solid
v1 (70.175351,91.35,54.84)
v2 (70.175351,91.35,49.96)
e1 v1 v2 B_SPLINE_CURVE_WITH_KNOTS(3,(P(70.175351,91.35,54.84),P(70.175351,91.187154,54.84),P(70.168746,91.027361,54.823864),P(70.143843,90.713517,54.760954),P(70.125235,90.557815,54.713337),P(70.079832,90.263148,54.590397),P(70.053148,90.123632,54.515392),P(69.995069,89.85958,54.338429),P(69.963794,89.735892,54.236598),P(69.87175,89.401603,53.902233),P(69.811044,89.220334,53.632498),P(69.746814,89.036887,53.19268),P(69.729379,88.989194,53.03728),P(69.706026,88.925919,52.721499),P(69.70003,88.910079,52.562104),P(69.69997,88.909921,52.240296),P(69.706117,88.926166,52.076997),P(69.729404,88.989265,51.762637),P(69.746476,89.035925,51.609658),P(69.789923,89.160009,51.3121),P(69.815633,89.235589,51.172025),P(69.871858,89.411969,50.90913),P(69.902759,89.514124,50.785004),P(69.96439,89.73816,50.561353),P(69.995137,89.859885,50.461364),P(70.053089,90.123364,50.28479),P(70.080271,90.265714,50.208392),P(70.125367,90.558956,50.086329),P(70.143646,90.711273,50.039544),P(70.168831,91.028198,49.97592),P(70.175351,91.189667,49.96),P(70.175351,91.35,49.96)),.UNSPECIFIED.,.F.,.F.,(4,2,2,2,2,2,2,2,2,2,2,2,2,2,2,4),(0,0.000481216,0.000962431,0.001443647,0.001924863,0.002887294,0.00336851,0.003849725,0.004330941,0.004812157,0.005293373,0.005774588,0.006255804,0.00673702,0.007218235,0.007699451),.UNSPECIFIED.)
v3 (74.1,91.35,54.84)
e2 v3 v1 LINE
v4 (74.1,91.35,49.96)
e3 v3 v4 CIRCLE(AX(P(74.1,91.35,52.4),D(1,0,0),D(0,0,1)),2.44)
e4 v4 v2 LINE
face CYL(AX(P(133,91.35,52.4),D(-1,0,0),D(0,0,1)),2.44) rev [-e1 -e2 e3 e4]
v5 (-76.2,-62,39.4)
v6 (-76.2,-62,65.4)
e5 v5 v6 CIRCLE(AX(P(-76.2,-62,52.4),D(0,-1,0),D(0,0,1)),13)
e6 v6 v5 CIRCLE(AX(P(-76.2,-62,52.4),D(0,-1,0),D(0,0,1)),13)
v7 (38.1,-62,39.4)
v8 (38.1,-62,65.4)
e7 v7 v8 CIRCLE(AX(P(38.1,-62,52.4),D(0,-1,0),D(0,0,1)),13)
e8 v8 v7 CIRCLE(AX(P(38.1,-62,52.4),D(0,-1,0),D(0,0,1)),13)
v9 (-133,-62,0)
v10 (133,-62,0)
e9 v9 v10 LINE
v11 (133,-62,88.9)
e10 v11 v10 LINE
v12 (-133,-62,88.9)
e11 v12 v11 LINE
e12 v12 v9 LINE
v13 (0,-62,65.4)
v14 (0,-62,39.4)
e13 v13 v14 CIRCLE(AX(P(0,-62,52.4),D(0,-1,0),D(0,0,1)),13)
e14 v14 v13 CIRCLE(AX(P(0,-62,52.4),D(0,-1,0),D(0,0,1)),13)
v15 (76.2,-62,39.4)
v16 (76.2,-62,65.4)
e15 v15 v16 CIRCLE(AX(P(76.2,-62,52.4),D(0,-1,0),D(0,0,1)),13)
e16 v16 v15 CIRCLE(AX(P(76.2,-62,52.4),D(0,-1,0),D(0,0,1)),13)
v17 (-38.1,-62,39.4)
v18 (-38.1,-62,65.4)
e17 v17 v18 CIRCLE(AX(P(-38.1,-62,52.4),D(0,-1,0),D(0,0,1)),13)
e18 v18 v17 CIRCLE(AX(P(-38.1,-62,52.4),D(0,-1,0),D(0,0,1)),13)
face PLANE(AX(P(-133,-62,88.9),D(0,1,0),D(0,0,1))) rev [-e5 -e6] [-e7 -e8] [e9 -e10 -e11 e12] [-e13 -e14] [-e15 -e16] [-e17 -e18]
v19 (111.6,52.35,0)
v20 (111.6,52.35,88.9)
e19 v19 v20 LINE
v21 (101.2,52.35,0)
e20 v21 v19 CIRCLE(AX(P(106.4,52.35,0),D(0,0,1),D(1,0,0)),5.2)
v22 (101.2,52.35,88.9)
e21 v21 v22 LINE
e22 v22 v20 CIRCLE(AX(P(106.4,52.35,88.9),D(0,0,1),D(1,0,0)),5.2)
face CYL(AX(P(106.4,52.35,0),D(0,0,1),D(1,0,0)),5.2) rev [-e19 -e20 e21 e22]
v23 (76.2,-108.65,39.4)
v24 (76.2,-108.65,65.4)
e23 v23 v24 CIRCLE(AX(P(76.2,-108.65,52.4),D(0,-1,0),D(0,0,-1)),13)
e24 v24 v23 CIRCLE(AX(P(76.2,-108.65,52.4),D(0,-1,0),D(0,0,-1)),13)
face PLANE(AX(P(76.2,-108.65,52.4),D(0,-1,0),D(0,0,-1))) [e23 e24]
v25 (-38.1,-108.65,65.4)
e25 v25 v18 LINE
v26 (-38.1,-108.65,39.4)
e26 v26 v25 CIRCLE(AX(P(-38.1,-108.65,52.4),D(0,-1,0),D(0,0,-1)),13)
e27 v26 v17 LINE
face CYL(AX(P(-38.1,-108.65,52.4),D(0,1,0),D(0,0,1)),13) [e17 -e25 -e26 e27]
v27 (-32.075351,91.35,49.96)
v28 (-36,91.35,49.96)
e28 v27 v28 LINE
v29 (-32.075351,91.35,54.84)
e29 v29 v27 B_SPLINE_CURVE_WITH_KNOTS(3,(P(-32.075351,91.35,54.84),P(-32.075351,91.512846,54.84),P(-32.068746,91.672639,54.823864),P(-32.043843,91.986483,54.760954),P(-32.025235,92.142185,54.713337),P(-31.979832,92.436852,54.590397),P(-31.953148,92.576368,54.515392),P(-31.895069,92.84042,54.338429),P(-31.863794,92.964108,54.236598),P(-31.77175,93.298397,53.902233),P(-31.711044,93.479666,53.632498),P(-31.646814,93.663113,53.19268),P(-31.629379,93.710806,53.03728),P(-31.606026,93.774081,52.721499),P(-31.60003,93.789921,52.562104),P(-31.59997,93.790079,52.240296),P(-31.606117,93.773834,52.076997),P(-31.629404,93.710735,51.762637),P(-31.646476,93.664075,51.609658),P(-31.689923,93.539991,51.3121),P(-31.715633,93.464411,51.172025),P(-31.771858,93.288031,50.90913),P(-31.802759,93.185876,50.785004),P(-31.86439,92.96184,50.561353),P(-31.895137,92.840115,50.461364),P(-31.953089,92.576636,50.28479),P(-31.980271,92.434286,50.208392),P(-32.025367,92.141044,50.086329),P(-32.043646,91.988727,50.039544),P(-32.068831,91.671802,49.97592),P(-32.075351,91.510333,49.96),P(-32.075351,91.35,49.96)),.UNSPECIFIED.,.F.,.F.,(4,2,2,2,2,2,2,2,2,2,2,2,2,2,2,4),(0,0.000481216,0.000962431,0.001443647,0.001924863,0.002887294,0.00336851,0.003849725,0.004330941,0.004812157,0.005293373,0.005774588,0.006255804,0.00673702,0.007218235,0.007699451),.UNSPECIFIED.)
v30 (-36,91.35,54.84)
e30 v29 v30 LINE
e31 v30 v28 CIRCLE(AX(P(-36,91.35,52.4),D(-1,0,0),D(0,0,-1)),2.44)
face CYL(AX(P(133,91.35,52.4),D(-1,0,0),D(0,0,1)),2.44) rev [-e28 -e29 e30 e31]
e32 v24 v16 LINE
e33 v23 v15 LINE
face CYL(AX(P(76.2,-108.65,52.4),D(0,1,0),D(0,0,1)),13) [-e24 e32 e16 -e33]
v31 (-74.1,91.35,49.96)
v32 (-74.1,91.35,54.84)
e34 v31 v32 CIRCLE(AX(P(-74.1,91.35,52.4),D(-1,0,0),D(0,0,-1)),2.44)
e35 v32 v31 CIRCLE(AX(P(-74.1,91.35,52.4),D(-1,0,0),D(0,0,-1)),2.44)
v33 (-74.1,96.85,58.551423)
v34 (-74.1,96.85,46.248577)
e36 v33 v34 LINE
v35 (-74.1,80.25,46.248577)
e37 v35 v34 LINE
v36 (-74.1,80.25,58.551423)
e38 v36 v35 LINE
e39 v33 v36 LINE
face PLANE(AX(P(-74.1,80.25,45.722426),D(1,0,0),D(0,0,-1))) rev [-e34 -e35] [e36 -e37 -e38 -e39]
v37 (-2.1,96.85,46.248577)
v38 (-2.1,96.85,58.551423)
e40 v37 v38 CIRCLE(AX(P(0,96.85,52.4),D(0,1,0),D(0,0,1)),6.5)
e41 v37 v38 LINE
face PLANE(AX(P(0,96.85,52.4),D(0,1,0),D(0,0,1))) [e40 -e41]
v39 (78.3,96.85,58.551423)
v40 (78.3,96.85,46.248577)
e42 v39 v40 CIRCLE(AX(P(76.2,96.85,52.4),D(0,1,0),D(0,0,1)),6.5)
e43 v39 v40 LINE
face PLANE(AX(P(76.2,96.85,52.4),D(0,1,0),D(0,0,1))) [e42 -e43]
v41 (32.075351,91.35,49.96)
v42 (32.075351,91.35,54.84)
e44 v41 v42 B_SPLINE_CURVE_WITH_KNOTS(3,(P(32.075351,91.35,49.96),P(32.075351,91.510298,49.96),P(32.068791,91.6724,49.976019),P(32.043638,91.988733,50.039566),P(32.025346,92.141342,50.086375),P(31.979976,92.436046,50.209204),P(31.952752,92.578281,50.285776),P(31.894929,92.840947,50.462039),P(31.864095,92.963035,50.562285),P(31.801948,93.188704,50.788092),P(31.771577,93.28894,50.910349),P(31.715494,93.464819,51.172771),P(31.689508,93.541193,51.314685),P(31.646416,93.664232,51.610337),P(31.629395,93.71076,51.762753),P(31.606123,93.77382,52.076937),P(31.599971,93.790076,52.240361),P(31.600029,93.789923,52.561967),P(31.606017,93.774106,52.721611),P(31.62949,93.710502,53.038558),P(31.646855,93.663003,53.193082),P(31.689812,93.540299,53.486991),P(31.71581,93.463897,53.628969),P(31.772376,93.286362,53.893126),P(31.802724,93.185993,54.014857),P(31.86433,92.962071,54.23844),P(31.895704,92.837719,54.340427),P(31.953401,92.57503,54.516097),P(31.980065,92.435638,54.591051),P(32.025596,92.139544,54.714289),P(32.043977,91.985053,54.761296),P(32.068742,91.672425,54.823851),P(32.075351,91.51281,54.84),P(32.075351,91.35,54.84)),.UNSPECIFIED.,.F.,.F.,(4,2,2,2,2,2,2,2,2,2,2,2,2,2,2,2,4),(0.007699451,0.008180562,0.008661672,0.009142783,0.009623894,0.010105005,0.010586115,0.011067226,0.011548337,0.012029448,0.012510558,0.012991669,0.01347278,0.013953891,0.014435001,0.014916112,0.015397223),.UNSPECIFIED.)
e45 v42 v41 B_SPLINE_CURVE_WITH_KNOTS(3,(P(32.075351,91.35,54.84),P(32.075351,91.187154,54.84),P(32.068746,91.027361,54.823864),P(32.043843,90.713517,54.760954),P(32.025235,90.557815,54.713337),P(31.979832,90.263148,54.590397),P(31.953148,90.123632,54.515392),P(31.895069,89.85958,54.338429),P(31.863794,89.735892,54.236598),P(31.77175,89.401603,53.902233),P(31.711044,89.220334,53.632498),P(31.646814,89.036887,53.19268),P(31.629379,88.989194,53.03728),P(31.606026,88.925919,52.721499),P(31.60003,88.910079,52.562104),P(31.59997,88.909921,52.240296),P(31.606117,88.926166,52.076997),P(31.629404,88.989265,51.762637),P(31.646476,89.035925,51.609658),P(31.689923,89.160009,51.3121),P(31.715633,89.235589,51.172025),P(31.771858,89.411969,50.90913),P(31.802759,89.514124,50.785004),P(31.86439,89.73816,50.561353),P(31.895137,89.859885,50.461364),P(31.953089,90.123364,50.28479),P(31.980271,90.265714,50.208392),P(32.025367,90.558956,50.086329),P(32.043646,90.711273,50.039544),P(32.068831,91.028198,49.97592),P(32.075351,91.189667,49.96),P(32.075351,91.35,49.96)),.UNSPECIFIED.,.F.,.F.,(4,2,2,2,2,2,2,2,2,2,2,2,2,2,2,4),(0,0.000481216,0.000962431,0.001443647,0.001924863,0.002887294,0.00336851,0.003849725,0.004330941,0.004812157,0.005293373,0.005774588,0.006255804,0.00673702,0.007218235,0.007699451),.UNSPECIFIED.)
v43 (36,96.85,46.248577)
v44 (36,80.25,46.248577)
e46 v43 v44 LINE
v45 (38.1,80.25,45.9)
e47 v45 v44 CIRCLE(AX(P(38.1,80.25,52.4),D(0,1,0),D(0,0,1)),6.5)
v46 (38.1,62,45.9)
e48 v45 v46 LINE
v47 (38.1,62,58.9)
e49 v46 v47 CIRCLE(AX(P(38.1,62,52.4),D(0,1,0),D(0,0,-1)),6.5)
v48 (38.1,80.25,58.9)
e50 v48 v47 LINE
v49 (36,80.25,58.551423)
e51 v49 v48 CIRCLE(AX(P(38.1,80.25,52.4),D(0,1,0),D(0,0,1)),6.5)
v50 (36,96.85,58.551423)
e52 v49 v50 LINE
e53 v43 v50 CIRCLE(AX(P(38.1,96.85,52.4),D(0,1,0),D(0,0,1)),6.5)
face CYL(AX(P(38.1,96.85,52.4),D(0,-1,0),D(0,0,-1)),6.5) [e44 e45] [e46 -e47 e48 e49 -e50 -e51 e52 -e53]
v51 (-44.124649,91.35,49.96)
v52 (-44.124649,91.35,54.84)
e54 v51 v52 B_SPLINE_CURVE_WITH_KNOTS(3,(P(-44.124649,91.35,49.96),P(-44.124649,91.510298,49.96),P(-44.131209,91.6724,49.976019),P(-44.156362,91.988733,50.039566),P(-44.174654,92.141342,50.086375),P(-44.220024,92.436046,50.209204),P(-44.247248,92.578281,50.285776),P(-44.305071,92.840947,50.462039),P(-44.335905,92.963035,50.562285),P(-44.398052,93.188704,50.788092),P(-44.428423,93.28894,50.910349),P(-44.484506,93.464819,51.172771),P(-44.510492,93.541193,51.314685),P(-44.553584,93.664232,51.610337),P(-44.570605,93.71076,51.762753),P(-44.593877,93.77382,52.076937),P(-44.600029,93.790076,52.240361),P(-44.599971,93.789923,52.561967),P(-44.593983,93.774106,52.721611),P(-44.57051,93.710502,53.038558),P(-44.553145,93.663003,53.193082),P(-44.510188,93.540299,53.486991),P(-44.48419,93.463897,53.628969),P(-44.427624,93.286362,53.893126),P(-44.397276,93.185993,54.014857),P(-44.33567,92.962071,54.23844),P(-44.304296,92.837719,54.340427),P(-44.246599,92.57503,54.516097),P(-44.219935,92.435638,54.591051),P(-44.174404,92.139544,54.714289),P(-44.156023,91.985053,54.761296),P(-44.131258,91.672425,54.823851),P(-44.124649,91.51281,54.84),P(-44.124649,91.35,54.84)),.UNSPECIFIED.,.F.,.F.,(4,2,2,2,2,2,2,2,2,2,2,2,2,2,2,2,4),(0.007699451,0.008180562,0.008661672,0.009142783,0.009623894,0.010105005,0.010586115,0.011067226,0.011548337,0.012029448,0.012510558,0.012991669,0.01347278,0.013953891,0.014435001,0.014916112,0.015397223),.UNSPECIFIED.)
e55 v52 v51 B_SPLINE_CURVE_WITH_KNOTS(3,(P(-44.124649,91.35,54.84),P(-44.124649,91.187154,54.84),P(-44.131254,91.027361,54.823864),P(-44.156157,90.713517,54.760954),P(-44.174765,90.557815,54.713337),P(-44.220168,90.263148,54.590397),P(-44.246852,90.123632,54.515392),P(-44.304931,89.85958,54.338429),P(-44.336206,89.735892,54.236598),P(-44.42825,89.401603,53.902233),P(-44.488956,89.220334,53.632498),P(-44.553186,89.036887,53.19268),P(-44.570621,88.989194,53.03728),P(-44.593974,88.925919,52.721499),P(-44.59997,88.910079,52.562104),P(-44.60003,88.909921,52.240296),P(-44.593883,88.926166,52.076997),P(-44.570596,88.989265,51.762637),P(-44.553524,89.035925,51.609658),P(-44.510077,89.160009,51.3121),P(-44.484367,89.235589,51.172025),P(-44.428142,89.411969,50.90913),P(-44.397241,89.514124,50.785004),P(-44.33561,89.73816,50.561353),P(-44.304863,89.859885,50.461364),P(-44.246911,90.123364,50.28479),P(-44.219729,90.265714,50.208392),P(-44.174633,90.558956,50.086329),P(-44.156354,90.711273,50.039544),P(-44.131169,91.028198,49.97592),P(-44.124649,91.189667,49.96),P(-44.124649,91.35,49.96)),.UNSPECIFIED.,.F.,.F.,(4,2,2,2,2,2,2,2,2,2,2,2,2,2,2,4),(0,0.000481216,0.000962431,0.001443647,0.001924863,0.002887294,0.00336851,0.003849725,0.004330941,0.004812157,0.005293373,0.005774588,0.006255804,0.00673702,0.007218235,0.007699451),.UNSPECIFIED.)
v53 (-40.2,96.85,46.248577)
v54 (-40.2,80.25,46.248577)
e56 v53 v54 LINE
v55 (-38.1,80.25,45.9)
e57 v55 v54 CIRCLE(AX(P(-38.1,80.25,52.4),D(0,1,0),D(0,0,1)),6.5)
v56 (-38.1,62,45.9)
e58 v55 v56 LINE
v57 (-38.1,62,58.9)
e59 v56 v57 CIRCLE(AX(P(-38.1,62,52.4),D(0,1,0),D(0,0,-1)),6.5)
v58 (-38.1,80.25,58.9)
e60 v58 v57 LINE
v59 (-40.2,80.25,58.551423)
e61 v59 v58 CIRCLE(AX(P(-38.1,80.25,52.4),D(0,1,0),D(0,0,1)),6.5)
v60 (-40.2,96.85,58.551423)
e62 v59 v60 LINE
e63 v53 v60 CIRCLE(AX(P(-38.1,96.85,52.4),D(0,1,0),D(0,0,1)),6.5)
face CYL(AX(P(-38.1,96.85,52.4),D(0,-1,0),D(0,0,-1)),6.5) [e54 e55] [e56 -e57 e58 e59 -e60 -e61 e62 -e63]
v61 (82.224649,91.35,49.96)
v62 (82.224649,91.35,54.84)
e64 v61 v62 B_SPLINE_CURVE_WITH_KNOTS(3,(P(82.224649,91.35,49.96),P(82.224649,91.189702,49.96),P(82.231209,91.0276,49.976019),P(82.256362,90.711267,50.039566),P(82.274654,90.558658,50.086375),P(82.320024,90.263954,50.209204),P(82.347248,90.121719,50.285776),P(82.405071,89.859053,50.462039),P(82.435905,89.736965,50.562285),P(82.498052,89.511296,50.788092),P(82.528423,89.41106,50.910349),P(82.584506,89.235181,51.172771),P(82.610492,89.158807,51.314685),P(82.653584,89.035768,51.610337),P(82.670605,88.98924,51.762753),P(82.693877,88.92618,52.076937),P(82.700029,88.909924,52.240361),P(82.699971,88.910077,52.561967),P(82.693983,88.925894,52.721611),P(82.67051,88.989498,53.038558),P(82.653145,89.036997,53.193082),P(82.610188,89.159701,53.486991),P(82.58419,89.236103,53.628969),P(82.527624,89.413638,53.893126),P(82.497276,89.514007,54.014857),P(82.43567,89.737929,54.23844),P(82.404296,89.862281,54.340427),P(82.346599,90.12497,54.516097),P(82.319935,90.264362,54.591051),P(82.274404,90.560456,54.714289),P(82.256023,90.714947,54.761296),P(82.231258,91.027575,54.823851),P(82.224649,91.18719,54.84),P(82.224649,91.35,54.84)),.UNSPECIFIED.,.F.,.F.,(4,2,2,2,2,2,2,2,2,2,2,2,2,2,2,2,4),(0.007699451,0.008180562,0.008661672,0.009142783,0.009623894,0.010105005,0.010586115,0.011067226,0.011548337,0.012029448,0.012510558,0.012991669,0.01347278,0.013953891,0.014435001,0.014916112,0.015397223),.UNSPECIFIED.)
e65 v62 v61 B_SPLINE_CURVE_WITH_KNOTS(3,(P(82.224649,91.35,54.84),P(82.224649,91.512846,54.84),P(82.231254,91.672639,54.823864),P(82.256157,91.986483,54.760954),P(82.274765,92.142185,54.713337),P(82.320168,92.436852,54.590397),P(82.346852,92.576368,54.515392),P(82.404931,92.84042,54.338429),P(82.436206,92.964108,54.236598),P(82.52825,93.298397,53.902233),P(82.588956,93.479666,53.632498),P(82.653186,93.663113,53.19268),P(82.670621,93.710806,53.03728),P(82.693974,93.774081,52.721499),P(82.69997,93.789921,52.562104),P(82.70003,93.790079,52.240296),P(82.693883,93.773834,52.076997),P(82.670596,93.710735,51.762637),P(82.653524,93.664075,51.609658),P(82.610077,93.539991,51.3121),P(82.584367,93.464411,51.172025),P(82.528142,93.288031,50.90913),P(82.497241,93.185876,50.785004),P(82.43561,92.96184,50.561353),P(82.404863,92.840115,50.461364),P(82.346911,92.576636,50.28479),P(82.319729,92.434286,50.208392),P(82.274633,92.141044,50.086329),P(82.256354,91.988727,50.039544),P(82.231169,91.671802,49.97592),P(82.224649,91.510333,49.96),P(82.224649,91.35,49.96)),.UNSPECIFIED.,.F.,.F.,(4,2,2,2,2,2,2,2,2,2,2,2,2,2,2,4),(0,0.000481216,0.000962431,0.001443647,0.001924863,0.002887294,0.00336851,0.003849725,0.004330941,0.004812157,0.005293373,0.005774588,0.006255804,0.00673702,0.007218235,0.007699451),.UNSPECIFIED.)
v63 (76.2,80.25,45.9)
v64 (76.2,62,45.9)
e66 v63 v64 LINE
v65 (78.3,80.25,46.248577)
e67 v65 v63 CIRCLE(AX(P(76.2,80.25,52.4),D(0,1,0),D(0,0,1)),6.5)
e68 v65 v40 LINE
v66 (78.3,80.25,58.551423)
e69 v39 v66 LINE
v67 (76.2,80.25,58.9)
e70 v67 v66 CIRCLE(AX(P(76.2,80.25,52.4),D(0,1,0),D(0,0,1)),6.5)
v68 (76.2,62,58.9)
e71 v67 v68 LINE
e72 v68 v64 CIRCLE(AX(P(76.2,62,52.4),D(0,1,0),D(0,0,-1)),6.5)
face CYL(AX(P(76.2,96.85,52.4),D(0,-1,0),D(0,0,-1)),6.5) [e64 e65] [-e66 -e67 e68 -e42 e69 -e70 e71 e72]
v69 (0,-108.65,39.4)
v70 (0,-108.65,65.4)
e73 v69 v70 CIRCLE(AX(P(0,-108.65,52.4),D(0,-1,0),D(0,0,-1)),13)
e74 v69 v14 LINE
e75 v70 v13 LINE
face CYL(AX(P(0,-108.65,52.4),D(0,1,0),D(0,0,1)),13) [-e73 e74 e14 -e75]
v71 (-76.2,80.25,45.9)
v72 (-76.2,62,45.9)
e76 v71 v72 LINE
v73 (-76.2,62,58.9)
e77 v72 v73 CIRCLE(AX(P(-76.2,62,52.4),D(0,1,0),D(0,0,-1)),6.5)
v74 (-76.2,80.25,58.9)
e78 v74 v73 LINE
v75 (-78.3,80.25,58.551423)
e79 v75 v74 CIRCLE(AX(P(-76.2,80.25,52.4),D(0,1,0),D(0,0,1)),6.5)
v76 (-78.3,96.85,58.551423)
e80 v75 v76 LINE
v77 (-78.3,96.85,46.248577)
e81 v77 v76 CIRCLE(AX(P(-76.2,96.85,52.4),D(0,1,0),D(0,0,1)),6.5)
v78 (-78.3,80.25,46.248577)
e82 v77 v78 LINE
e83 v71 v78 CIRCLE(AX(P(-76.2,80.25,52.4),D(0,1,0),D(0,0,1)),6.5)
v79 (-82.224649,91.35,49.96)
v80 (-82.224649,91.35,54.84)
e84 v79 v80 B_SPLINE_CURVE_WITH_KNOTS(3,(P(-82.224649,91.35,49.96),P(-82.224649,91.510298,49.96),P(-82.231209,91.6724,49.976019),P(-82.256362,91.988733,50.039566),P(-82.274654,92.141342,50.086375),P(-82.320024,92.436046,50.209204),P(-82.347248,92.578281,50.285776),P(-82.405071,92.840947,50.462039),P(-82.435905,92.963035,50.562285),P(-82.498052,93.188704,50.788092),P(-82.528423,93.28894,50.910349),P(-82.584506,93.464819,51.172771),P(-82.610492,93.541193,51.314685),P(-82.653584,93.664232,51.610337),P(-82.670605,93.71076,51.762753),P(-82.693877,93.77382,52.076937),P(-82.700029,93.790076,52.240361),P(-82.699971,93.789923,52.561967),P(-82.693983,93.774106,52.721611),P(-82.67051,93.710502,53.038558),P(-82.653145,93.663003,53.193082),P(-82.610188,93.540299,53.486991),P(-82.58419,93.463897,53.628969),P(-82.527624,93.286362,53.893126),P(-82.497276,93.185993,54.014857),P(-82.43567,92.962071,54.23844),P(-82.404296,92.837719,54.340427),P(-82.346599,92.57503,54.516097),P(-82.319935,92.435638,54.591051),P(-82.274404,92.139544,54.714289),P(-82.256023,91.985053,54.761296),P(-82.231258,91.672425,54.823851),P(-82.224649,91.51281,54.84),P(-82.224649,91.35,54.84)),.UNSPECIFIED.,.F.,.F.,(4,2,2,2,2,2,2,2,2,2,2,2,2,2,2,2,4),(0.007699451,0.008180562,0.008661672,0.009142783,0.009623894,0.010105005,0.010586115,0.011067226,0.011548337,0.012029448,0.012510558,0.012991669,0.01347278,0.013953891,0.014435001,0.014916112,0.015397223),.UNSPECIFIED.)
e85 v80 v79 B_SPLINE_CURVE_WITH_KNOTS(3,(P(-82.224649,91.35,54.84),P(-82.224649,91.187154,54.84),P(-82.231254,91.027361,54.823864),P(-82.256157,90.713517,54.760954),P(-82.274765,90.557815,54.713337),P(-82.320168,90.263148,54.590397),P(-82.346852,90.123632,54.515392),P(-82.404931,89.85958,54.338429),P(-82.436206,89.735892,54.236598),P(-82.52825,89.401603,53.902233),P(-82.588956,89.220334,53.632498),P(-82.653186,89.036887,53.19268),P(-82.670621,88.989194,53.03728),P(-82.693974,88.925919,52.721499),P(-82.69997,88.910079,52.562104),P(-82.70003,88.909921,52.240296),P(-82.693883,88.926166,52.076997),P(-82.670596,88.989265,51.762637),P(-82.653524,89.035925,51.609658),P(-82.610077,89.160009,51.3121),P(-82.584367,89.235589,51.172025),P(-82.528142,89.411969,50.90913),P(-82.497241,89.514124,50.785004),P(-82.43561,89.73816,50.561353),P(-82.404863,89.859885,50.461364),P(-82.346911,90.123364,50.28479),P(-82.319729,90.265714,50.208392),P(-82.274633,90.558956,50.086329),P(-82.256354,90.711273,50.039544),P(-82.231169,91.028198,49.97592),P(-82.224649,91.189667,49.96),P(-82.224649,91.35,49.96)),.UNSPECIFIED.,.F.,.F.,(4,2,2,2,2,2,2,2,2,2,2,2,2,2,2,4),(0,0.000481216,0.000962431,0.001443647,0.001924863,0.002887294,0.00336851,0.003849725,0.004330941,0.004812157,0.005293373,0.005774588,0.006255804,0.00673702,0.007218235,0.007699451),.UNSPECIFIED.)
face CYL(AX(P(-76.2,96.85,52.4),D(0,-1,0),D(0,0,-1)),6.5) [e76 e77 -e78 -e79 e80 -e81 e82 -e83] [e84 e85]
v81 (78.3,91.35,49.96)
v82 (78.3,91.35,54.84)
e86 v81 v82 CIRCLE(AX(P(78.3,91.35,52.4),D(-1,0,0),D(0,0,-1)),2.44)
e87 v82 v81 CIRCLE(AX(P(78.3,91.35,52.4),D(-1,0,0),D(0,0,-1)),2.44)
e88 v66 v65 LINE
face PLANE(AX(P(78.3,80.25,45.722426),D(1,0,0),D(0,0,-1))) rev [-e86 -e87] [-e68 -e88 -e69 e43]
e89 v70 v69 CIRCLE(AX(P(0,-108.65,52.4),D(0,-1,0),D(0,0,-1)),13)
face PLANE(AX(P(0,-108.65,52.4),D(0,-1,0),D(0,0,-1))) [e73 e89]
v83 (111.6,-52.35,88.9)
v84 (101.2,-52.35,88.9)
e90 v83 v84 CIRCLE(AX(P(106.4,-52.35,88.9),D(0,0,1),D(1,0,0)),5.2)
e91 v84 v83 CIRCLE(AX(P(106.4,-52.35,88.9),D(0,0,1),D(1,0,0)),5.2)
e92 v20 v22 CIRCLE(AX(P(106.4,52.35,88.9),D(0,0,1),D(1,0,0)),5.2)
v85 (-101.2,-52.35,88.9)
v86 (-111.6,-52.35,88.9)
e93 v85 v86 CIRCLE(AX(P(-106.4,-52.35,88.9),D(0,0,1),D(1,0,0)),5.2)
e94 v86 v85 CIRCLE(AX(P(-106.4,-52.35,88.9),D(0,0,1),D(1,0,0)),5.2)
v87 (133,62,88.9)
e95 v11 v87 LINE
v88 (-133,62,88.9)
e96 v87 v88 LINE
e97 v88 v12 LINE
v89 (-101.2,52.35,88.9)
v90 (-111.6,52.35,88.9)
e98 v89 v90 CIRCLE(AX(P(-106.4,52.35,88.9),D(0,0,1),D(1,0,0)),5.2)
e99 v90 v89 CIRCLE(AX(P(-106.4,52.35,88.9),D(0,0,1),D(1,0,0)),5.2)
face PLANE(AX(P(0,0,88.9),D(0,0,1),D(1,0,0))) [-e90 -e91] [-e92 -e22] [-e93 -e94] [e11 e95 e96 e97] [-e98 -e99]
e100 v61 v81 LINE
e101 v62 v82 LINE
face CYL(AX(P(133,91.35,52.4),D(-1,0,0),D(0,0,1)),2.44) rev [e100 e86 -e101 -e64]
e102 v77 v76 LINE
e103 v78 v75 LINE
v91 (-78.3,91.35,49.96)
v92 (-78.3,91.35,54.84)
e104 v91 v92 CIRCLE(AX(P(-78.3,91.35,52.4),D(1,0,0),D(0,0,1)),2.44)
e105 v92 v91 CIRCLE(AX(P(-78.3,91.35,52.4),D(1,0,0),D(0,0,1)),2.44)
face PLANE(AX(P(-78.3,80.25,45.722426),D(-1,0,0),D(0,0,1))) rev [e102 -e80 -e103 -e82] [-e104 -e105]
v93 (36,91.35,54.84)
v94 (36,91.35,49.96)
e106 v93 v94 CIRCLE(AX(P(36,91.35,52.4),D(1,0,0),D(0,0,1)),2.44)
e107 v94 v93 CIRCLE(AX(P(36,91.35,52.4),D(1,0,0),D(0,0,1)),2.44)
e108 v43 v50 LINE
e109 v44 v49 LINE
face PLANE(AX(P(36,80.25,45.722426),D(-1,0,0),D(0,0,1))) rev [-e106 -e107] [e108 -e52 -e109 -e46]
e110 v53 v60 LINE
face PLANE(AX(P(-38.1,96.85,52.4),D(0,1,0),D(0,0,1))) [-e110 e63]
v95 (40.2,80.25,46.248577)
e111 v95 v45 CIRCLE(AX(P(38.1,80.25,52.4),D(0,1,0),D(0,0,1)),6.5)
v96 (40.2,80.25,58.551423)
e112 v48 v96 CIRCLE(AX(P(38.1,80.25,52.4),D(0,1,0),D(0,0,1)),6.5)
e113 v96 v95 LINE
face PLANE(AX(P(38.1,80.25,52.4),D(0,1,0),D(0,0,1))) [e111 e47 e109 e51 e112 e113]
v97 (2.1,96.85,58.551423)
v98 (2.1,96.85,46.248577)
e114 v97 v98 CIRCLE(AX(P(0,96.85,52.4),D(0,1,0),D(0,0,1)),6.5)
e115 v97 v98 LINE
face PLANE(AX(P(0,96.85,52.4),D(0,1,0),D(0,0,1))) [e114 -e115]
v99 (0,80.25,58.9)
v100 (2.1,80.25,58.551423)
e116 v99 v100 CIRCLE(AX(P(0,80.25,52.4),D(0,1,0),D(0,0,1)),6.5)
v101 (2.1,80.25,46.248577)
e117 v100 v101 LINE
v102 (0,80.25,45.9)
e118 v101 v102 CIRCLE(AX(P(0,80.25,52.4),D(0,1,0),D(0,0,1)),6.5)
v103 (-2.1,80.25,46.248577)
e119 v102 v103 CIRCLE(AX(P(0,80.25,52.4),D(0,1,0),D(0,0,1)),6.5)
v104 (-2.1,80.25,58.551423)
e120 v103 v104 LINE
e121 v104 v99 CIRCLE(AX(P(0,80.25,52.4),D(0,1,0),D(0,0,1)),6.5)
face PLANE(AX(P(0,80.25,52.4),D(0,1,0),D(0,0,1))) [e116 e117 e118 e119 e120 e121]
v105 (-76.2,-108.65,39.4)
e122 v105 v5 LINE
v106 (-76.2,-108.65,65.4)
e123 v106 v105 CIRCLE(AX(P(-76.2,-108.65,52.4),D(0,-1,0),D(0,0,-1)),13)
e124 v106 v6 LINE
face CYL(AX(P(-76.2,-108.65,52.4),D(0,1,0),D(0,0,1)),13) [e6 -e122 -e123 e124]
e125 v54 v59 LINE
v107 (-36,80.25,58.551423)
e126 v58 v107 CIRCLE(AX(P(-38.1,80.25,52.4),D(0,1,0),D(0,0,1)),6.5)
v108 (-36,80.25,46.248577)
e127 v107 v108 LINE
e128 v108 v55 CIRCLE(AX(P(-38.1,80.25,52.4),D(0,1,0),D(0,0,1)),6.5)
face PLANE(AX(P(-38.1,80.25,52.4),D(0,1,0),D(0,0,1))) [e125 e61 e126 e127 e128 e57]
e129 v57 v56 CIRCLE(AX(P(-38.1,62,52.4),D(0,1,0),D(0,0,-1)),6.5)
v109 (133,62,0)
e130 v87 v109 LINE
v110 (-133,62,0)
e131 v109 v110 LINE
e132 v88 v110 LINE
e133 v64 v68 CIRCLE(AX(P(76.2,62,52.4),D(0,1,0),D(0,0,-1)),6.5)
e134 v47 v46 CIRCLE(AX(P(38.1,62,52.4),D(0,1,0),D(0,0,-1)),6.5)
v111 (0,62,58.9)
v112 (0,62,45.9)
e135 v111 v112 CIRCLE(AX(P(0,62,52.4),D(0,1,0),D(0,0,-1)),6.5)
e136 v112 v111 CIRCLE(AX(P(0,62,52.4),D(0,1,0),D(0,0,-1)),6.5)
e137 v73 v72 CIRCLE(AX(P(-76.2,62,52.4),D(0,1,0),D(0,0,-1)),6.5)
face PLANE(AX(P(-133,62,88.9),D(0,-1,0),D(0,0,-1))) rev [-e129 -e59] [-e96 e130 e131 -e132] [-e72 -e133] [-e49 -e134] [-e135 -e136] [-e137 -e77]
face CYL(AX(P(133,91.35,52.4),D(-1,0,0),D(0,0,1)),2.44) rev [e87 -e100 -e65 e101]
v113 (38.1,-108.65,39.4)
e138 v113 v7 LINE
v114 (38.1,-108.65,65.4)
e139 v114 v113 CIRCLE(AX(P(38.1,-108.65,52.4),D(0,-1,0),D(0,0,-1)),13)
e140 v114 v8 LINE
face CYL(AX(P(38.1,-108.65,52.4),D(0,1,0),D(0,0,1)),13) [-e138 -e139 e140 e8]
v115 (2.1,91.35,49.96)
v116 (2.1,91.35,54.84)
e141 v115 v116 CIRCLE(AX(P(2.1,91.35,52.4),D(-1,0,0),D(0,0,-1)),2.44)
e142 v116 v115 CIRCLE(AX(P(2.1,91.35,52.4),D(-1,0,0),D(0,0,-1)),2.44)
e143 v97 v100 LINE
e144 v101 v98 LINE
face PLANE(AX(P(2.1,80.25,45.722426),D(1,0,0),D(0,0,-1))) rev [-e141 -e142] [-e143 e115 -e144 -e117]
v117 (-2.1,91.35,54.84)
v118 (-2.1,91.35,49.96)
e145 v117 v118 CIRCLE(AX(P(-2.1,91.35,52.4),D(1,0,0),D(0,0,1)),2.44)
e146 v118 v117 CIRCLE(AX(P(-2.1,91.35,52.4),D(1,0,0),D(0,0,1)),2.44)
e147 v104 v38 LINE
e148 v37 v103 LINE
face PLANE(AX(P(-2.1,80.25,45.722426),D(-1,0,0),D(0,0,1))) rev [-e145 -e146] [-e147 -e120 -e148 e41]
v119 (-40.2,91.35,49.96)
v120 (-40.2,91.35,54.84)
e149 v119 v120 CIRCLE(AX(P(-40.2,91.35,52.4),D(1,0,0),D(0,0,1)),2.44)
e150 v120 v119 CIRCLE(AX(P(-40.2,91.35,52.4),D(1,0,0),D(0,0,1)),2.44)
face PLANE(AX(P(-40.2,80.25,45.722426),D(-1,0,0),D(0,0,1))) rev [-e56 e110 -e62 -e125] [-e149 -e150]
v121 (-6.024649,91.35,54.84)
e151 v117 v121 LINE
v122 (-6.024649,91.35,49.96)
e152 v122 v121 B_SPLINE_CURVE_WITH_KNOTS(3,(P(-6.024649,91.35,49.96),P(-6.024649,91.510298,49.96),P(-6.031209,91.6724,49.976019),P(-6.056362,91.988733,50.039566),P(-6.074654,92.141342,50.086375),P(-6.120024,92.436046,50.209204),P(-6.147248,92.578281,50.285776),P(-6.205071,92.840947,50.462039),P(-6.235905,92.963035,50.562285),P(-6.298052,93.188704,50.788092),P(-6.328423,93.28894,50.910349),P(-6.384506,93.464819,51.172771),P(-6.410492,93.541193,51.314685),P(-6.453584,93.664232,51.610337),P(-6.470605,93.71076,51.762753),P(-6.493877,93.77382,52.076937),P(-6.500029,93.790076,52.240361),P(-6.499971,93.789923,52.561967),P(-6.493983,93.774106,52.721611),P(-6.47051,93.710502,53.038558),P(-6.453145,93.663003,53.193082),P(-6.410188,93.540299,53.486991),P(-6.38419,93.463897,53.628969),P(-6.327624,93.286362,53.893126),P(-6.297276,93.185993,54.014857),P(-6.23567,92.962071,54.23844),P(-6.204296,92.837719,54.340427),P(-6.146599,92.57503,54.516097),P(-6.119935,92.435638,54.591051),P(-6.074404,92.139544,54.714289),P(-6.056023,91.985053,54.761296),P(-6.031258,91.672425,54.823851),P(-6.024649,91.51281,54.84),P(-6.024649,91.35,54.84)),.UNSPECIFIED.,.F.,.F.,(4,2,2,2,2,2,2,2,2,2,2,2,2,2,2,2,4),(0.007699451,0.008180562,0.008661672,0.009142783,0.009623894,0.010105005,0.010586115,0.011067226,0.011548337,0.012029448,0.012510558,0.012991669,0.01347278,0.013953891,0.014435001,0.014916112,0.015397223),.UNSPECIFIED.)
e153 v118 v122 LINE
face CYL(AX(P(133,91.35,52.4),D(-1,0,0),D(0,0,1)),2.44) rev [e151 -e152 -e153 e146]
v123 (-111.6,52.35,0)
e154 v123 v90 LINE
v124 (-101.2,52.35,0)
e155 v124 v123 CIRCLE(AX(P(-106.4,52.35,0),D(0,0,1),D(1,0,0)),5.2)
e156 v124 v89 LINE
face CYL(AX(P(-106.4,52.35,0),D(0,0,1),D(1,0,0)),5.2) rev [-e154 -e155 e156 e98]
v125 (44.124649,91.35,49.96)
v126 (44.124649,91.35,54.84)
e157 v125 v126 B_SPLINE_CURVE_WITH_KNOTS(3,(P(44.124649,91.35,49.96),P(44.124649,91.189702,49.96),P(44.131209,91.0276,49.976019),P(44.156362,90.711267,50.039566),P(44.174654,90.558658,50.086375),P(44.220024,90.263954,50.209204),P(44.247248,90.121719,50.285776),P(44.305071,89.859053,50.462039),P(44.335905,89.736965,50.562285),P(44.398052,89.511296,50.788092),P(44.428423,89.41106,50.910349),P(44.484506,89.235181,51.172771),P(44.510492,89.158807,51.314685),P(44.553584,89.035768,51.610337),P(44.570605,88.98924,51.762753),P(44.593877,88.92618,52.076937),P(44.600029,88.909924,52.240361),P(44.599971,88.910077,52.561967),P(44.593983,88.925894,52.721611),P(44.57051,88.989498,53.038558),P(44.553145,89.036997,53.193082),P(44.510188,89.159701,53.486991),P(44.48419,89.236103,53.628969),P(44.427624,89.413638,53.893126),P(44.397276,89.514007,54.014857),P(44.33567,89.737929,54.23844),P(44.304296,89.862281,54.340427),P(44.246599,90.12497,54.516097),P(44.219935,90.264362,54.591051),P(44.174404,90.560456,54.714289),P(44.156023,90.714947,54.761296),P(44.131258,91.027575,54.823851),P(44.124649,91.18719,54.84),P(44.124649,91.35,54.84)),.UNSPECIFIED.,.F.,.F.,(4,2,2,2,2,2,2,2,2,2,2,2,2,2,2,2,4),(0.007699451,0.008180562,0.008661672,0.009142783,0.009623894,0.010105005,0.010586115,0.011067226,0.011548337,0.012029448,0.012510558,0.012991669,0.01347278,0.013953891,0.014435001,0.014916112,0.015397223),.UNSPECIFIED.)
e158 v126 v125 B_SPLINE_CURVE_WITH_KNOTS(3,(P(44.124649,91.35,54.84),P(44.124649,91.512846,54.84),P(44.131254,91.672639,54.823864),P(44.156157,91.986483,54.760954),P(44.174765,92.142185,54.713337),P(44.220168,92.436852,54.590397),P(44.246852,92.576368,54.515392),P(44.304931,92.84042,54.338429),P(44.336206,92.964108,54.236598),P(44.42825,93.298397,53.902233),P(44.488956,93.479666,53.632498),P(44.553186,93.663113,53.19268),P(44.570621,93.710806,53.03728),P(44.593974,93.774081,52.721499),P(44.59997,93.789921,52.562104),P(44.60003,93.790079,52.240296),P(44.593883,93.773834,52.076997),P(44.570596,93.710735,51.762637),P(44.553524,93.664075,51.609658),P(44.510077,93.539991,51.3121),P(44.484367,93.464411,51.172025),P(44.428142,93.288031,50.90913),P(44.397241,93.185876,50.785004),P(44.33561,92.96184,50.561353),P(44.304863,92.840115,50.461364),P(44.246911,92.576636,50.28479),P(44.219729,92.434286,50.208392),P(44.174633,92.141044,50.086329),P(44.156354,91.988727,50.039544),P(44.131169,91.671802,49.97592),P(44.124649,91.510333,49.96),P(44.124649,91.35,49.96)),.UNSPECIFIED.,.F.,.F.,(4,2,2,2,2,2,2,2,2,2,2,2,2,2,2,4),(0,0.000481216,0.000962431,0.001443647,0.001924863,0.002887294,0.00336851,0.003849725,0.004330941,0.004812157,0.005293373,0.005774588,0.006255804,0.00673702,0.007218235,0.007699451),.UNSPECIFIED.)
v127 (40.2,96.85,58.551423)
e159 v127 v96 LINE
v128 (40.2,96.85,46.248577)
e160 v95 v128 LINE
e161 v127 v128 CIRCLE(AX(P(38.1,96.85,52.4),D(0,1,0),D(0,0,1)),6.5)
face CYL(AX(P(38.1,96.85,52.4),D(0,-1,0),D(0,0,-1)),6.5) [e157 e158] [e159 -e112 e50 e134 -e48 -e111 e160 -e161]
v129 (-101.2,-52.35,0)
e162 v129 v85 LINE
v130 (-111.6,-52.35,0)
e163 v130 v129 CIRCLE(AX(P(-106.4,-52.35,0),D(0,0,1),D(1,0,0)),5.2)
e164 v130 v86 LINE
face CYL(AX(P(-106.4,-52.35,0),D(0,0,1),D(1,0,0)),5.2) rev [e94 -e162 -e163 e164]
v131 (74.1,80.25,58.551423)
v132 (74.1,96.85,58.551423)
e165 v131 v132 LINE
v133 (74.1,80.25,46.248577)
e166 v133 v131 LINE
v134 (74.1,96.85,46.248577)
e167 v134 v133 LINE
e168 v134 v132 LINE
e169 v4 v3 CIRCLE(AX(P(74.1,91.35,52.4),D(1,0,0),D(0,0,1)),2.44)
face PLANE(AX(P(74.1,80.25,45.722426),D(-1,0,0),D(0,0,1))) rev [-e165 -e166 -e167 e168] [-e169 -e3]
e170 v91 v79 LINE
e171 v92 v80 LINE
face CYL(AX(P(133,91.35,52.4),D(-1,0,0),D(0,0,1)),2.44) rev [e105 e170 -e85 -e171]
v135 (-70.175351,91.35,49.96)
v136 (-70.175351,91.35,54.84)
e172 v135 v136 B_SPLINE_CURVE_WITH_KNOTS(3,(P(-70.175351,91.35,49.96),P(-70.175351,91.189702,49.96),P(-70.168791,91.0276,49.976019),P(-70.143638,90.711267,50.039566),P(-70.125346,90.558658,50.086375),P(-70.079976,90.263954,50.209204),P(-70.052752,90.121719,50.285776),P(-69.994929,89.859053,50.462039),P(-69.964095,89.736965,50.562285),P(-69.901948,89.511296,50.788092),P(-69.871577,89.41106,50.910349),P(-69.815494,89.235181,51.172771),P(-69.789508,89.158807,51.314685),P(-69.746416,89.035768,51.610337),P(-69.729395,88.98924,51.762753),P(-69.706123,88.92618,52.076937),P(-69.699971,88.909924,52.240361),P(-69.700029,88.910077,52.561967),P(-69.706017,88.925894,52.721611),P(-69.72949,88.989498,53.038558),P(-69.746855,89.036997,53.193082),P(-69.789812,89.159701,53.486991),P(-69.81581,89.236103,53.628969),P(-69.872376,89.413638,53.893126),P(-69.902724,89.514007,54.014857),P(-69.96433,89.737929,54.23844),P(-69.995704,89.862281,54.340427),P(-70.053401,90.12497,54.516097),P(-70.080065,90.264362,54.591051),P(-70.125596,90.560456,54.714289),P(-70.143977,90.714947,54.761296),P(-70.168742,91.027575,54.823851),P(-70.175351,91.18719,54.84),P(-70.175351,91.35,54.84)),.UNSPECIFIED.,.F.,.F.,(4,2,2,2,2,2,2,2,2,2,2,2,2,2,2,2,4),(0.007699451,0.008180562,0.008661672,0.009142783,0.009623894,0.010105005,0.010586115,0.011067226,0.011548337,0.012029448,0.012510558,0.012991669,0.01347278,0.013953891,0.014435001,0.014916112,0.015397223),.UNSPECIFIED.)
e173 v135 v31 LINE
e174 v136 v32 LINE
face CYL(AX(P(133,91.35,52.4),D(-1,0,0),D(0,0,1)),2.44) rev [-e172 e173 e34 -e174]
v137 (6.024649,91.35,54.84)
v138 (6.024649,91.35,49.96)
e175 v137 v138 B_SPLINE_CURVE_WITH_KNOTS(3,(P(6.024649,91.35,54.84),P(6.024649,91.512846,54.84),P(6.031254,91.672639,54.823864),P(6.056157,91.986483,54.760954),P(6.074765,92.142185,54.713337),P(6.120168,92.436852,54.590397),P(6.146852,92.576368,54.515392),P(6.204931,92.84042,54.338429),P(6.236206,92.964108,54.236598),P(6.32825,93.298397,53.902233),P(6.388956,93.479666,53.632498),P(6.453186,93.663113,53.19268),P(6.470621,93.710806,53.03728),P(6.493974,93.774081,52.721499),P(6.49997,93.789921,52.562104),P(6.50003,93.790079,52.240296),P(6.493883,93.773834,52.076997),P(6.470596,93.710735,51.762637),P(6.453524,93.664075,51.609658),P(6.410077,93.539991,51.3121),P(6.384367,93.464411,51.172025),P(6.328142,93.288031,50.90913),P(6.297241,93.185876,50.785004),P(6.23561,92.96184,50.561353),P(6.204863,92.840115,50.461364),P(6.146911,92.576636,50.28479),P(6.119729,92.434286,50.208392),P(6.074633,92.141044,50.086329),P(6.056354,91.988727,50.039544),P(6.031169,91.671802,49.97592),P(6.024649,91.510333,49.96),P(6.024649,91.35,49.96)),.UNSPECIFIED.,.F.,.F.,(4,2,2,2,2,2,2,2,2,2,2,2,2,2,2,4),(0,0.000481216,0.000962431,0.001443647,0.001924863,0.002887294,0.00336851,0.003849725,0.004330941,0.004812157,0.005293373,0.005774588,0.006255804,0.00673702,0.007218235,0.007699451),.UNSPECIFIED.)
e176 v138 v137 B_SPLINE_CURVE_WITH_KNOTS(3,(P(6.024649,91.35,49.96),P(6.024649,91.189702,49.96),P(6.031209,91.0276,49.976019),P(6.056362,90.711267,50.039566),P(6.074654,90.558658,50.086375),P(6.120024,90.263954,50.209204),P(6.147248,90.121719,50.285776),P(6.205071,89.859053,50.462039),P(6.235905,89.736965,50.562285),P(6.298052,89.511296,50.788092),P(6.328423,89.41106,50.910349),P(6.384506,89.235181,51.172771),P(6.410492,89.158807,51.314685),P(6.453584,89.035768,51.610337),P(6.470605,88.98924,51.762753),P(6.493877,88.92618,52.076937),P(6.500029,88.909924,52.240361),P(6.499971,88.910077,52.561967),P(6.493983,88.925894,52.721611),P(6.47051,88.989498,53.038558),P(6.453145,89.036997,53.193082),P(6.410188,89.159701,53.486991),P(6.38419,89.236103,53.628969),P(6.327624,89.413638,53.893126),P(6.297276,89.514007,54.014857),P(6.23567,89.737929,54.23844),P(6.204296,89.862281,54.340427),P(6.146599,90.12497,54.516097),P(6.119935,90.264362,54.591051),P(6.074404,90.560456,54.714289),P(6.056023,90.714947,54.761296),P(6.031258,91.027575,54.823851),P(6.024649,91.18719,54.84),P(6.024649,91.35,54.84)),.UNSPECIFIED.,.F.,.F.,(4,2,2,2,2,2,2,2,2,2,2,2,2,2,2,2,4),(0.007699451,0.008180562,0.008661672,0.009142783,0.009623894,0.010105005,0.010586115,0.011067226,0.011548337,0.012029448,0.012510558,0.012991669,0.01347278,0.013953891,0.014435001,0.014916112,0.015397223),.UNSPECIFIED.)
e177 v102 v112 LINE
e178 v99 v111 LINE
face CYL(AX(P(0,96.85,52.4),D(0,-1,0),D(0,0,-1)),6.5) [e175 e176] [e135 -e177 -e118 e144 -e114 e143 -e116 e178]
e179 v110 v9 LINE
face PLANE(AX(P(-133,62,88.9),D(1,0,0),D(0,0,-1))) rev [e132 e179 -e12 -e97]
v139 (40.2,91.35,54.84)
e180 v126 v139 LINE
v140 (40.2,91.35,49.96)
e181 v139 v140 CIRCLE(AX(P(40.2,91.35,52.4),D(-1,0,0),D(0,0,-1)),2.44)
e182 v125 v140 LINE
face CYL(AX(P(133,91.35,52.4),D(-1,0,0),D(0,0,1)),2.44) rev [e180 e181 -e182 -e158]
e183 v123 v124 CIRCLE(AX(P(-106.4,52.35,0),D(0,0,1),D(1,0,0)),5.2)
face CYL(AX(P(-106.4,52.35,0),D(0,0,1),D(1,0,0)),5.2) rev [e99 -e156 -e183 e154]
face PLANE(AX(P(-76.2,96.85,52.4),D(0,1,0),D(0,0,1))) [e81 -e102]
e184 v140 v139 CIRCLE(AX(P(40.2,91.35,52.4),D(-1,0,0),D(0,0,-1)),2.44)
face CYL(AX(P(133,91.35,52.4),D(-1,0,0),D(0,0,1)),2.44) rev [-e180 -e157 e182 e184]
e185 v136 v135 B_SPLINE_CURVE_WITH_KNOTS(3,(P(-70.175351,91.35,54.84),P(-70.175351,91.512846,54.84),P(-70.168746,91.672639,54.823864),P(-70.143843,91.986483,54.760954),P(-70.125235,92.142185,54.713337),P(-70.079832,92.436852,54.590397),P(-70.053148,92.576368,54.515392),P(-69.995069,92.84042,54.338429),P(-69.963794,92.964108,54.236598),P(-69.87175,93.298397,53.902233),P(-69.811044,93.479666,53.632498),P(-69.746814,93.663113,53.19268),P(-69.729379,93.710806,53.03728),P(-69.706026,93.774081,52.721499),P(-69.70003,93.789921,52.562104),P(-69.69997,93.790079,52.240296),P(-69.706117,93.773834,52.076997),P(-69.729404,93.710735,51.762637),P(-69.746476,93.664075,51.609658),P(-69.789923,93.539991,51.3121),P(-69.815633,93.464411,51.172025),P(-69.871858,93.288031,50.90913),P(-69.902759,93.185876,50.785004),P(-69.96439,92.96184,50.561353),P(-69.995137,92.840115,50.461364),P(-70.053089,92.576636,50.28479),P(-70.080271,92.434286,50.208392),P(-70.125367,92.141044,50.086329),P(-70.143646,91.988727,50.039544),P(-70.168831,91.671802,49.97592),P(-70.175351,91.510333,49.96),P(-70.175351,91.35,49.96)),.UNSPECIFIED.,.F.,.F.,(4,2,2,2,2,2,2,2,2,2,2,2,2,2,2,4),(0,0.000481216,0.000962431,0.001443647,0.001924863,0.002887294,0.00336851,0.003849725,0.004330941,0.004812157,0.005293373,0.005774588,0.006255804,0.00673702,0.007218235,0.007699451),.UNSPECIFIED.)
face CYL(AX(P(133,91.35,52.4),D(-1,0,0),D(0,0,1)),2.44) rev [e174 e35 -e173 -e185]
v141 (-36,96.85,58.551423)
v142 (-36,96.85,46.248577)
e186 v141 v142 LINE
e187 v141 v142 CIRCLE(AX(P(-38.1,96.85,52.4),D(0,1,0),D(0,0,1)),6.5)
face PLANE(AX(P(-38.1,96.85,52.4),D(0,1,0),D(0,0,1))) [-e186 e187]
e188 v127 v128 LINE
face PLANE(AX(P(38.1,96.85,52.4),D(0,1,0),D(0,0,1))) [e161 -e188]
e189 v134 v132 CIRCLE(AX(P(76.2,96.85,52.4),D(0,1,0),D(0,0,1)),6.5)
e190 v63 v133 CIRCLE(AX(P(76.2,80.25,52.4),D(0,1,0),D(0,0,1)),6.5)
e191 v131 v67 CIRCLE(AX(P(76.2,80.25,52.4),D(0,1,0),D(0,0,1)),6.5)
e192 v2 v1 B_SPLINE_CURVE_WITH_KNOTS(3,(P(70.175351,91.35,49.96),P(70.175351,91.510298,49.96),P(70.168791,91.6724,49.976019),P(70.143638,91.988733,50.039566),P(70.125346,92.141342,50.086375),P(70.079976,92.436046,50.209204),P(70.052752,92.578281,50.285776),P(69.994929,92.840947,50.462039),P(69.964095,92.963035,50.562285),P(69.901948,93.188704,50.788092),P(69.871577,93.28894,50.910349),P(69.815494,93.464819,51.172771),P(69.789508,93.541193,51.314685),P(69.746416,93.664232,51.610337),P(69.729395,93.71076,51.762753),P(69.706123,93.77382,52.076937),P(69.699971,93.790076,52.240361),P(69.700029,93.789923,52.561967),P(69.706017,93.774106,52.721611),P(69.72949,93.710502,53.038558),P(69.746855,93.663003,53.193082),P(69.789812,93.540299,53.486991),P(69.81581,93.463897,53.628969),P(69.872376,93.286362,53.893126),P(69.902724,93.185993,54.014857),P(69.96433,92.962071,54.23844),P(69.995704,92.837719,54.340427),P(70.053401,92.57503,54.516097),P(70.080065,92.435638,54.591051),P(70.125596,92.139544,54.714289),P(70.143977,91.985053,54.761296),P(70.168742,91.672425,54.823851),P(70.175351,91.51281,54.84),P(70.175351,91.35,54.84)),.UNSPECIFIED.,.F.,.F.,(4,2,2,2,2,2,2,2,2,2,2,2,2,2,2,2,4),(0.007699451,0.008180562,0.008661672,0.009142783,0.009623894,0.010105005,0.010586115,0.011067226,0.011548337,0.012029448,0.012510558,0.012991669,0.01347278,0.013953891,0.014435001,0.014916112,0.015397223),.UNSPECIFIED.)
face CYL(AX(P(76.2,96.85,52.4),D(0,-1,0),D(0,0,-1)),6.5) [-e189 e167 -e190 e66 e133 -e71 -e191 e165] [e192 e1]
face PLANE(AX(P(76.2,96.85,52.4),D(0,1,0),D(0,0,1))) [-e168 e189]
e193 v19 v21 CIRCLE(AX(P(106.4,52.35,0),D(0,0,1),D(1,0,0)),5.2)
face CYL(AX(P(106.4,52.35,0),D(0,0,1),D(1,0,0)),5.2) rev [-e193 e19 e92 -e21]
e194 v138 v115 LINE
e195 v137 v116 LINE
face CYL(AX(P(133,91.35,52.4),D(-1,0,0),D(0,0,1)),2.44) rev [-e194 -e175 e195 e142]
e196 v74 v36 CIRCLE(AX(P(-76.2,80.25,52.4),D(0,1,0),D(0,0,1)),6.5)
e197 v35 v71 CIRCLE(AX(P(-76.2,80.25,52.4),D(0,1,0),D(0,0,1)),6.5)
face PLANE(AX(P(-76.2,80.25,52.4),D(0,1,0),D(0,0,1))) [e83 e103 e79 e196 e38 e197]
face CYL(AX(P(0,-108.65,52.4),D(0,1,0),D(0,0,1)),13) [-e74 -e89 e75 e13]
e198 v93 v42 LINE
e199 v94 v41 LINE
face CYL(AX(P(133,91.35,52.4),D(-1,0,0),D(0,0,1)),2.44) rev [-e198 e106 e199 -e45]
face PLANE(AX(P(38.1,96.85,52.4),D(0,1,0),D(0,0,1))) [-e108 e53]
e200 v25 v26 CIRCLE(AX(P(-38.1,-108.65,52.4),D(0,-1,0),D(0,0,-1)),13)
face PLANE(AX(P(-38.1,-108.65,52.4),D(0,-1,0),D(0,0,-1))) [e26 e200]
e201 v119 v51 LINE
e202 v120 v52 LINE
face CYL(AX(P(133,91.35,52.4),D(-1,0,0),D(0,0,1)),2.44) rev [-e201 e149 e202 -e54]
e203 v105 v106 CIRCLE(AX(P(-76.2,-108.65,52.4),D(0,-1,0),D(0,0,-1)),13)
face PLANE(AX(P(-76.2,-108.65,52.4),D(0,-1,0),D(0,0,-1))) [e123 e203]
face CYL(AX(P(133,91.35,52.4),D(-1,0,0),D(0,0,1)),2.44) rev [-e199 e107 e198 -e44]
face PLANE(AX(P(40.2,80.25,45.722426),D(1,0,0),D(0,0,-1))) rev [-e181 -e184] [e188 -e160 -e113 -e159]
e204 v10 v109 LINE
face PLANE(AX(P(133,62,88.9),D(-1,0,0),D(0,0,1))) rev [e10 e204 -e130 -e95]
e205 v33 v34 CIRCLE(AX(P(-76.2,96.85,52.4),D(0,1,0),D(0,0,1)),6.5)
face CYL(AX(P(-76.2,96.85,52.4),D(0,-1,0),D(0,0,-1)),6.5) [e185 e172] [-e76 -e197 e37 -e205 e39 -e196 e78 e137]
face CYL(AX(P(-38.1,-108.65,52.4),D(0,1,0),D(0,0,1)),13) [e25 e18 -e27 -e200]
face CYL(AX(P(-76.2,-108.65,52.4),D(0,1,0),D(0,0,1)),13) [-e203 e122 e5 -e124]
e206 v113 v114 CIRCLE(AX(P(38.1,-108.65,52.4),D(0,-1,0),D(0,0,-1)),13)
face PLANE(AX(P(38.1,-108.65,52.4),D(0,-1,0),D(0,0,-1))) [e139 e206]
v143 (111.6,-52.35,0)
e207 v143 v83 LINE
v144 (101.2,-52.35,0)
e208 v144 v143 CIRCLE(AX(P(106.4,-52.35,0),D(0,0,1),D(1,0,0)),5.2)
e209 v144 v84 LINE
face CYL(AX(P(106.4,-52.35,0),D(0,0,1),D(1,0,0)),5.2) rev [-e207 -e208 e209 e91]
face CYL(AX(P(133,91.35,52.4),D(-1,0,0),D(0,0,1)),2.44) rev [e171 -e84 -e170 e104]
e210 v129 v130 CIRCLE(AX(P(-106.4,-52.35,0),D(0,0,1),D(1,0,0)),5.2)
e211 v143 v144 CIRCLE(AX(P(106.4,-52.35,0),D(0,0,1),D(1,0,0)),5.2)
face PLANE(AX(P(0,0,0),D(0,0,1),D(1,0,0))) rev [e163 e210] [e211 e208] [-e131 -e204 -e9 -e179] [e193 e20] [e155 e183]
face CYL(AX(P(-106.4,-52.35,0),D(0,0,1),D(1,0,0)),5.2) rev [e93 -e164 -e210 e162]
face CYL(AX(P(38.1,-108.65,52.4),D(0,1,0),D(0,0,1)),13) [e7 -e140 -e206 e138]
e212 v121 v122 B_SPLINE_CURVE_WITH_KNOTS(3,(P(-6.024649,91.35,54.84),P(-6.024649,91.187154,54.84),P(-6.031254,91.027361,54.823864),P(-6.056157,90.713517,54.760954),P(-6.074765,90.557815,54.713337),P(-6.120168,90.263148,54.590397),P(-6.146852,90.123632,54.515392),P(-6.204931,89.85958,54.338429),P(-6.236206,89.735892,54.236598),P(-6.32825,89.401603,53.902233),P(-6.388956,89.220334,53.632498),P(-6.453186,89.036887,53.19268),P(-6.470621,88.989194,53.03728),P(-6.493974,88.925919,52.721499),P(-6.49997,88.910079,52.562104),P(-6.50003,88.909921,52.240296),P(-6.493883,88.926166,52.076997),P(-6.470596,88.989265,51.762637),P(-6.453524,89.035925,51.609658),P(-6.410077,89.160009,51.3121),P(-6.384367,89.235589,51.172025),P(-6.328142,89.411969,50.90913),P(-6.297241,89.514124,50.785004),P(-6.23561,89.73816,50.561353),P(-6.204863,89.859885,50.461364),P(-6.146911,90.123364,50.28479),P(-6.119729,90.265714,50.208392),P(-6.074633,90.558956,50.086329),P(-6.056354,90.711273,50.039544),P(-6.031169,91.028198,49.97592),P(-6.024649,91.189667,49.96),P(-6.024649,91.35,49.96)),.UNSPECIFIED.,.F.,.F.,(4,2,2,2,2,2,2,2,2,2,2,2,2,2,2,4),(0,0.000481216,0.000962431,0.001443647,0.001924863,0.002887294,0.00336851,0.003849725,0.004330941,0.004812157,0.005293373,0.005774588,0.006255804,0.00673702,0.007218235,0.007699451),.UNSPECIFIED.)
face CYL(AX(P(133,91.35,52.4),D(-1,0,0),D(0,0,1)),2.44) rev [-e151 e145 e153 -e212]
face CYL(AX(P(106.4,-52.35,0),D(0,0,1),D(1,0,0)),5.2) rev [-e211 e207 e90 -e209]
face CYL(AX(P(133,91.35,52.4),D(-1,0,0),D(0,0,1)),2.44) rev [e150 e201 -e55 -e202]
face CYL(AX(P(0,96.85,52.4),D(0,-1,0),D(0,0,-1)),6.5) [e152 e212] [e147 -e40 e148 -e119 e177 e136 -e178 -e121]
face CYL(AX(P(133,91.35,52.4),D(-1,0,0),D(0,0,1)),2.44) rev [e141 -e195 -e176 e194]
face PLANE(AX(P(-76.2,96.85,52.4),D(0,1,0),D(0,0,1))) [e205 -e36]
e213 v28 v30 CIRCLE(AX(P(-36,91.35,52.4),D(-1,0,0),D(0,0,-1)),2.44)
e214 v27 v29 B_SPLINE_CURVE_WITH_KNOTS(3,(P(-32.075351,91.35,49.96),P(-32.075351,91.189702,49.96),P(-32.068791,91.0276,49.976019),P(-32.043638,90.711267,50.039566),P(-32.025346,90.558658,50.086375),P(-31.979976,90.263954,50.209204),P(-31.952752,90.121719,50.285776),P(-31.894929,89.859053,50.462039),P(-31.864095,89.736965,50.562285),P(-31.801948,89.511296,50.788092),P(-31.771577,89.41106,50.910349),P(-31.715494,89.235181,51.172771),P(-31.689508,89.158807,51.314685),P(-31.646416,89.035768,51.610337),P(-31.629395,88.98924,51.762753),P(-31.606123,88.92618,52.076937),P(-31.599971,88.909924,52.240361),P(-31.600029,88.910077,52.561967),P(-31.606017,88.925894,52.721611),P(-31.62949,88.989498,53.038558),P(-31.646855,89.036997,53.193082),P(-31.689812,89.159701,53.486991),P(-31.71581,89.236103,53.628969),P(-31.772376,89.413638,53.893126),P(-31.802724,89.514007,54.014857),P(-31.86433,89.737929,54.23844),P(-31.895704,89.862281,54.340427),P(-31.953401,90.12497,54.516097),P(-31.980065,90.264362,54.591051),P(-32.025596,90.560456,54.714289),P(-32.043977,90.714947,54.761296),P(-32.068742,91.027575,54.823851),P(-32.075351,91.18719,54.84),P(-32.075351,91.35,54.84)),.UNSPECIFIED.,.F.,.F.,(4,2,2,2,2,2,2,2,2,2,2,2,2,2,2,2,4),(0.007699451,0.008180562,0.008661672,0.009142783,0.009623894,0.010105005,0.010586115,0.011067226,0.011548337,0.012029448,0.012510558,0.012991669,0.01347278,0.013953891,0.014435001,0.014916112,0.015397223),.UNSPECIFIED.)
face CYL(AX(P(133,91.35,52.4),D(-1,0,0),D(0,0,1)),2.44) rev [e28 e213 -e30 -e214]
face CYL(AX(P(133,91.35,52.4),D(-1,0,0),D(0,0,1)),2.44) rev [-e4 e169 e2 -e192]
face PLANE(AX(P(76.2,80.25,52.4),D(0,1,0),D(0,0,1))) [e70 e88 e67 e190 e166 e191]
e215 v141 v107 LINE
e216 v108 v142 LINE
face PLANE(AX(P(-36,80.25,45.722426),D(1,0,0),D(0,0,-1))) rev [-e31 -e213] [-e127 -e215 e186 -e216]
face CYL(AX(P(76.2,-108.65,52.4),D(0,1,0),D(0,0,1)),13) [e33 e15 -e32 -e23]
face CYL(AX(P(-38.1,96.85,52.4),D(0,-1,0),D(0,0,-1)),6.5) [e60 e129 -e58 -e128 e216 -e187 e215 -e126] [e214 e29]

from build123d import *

# Parameters (mm, degrees)
SKETCH1_W            = 266
SKETCH1_H            = 124
BOSS_EXTRUDE1_DEPTH  = 88.9
SKETCH2_R            = 5.2
CUT_EXTRUDE1_DEPTH   = 88.9
LPATTERN1_COUNT      = 52
LPATTERN1_PITCH      = 212.8
LPATTERN1_COUNT_DIR2 = 2
LPATTERN1_PITCH_DIR2 = 104.7
SKETCH3_R            = 6.5
BOSS_EXTRUDE2_DEPTH  = 34.85
LPATTERN2_COUNT      = 5
LPATTERN2_PITCH      = 38.1
SKETCH6_R            = 13
BOSS_EXTRUDE3_DEPTH  = 46.65
LPATTERN5_COUNT      = 5
LPATTERN5_PITCH      = 38.1
SKETCH7_R            = 2.44
CUT_EXTRUDE2_DEPTH   = 301.772393181
CUT_EXTRUDE3_DEPTH   = 16.6
LPATTERN6_COUNT      = 5
LPATTERN6_PITCH      = 38.1


with BuildPart() as part:
    # Sketch1 → Boss-Extrude1 (new body)
    with BuildSketch(Plane.XY):
        Rectangle(SKETCH1_W, SKETCH1_H)
    extrude(amount=BOSS_EXTRUDE1_DEPTH)

    # Sketch2 → Cut-Extrude1 (cut)
    with BuildSketch(Plane.XY.offset(88.9)):
        with Locations((-106.4, 52.35)):
            Circle(SKETCH2_R)
    cut_extrude1 = extrude(amount=-CUT_EXTRUDE1_DEPTH, mode=Mode.SUBTRACT)

    # LPattern1: Cut-Extrude1 52 × 2
    with Locations(*[(i * LPATTERN1_PITCH, -j * LPATTERN1_PITCH_DIR2, 0) for i in range(LPATTERN1_COUNT) for j in range(LPATTERN1_COUNT_DIR2) if (i, j) != (0, 0)]):
        add(cut_extrude1, mode=Mode.SUBTRACT)

    # Sketch3 → Boss-Extrude2 (add)
    with BuildSketch(Plane(origin=(0, 62, 0), x_dir=(1, 0, 0), z_dir=(0, 1, 0))):
        with Locations(Location((-76.2, -52.4, 0), (0, 0, 90))):
            Circle(SKETCH3_R)
    boss_extrude2 = extrude(amount=BOSS_EXTRUDE2_DEPTH)

    # LPattern2: Boss-Extrude2 ×5
    with Locations(*[(i * LPATTERN2_PITCH, 0, 0) for i in range(1, LPATTERN2_COUNT)]):
        add(boss_extrude2)

    # Sketch6 → Boss-Extrude3 (add)
    with BuildSketch(Plane.XZ.offset(62)):
        with Locations(Location((-76.2, 52.4, 0), (0, 0, 90))):
            Circle(SKETCH6_R)
    boss_extrude3 = extrude(amount=BOSS_EXTRUDE3_DEPTH)

    # LPattern5: Boss-Extrude3 ×5
    with Locations(*[(i * LPATTERN5_PITCH, 0, 0) for i in range(1, LPATTERN5_COUNT)]):
        add(boss_extrude3)

    # Sketch7 → Cut-Extrude2 (cut, through all)
    with BuildSketch(Plane.ZY.offset(133)):
        with Locations((52.4, 91.35)):
            Circle(SKETCH7_R)
    extrude(amount=-CUT_EXTRUDE2_DEPTH, mode=Mode.SUBTRACT)

    # Sketch8 → Cut-Extrude3 (cut)
    with BuildSketch(Plane(origin=(0, 96.85, 0), x_dir=(1, 0, 0), z_dir=(0, 1, 0))):
        with BuildLine():
            Line((-78.3, -45.72242559), (-78.3, -59.07757441))
            ThreePointArc((-78.3, -59.07757441), (-76.2, -59.4), (-74.1, -59.07757441))
            Line((-74.1, -59.07757441), (-74.1, -45.72242559))
            ThreePointArc((-74.1, -45.72242559), (-76.2, -45.4), (-78.3, -45.72242559))
        make_face()
    cut_extrude3 = extrude(amount=-CUT_EXTRUDE3_DEPTH, mode=Mode.SUBTRACT)

    # LPattern6: Cut-Extrude3 ×5
    with Locations(*[(i * LPATTERN6_PITCH, 0, 0) for i in range(1, LPATTERN6_COUNT)]):
        add(cut_extrude3, mode=Mode.SUBTRACT)


solid = part.part
